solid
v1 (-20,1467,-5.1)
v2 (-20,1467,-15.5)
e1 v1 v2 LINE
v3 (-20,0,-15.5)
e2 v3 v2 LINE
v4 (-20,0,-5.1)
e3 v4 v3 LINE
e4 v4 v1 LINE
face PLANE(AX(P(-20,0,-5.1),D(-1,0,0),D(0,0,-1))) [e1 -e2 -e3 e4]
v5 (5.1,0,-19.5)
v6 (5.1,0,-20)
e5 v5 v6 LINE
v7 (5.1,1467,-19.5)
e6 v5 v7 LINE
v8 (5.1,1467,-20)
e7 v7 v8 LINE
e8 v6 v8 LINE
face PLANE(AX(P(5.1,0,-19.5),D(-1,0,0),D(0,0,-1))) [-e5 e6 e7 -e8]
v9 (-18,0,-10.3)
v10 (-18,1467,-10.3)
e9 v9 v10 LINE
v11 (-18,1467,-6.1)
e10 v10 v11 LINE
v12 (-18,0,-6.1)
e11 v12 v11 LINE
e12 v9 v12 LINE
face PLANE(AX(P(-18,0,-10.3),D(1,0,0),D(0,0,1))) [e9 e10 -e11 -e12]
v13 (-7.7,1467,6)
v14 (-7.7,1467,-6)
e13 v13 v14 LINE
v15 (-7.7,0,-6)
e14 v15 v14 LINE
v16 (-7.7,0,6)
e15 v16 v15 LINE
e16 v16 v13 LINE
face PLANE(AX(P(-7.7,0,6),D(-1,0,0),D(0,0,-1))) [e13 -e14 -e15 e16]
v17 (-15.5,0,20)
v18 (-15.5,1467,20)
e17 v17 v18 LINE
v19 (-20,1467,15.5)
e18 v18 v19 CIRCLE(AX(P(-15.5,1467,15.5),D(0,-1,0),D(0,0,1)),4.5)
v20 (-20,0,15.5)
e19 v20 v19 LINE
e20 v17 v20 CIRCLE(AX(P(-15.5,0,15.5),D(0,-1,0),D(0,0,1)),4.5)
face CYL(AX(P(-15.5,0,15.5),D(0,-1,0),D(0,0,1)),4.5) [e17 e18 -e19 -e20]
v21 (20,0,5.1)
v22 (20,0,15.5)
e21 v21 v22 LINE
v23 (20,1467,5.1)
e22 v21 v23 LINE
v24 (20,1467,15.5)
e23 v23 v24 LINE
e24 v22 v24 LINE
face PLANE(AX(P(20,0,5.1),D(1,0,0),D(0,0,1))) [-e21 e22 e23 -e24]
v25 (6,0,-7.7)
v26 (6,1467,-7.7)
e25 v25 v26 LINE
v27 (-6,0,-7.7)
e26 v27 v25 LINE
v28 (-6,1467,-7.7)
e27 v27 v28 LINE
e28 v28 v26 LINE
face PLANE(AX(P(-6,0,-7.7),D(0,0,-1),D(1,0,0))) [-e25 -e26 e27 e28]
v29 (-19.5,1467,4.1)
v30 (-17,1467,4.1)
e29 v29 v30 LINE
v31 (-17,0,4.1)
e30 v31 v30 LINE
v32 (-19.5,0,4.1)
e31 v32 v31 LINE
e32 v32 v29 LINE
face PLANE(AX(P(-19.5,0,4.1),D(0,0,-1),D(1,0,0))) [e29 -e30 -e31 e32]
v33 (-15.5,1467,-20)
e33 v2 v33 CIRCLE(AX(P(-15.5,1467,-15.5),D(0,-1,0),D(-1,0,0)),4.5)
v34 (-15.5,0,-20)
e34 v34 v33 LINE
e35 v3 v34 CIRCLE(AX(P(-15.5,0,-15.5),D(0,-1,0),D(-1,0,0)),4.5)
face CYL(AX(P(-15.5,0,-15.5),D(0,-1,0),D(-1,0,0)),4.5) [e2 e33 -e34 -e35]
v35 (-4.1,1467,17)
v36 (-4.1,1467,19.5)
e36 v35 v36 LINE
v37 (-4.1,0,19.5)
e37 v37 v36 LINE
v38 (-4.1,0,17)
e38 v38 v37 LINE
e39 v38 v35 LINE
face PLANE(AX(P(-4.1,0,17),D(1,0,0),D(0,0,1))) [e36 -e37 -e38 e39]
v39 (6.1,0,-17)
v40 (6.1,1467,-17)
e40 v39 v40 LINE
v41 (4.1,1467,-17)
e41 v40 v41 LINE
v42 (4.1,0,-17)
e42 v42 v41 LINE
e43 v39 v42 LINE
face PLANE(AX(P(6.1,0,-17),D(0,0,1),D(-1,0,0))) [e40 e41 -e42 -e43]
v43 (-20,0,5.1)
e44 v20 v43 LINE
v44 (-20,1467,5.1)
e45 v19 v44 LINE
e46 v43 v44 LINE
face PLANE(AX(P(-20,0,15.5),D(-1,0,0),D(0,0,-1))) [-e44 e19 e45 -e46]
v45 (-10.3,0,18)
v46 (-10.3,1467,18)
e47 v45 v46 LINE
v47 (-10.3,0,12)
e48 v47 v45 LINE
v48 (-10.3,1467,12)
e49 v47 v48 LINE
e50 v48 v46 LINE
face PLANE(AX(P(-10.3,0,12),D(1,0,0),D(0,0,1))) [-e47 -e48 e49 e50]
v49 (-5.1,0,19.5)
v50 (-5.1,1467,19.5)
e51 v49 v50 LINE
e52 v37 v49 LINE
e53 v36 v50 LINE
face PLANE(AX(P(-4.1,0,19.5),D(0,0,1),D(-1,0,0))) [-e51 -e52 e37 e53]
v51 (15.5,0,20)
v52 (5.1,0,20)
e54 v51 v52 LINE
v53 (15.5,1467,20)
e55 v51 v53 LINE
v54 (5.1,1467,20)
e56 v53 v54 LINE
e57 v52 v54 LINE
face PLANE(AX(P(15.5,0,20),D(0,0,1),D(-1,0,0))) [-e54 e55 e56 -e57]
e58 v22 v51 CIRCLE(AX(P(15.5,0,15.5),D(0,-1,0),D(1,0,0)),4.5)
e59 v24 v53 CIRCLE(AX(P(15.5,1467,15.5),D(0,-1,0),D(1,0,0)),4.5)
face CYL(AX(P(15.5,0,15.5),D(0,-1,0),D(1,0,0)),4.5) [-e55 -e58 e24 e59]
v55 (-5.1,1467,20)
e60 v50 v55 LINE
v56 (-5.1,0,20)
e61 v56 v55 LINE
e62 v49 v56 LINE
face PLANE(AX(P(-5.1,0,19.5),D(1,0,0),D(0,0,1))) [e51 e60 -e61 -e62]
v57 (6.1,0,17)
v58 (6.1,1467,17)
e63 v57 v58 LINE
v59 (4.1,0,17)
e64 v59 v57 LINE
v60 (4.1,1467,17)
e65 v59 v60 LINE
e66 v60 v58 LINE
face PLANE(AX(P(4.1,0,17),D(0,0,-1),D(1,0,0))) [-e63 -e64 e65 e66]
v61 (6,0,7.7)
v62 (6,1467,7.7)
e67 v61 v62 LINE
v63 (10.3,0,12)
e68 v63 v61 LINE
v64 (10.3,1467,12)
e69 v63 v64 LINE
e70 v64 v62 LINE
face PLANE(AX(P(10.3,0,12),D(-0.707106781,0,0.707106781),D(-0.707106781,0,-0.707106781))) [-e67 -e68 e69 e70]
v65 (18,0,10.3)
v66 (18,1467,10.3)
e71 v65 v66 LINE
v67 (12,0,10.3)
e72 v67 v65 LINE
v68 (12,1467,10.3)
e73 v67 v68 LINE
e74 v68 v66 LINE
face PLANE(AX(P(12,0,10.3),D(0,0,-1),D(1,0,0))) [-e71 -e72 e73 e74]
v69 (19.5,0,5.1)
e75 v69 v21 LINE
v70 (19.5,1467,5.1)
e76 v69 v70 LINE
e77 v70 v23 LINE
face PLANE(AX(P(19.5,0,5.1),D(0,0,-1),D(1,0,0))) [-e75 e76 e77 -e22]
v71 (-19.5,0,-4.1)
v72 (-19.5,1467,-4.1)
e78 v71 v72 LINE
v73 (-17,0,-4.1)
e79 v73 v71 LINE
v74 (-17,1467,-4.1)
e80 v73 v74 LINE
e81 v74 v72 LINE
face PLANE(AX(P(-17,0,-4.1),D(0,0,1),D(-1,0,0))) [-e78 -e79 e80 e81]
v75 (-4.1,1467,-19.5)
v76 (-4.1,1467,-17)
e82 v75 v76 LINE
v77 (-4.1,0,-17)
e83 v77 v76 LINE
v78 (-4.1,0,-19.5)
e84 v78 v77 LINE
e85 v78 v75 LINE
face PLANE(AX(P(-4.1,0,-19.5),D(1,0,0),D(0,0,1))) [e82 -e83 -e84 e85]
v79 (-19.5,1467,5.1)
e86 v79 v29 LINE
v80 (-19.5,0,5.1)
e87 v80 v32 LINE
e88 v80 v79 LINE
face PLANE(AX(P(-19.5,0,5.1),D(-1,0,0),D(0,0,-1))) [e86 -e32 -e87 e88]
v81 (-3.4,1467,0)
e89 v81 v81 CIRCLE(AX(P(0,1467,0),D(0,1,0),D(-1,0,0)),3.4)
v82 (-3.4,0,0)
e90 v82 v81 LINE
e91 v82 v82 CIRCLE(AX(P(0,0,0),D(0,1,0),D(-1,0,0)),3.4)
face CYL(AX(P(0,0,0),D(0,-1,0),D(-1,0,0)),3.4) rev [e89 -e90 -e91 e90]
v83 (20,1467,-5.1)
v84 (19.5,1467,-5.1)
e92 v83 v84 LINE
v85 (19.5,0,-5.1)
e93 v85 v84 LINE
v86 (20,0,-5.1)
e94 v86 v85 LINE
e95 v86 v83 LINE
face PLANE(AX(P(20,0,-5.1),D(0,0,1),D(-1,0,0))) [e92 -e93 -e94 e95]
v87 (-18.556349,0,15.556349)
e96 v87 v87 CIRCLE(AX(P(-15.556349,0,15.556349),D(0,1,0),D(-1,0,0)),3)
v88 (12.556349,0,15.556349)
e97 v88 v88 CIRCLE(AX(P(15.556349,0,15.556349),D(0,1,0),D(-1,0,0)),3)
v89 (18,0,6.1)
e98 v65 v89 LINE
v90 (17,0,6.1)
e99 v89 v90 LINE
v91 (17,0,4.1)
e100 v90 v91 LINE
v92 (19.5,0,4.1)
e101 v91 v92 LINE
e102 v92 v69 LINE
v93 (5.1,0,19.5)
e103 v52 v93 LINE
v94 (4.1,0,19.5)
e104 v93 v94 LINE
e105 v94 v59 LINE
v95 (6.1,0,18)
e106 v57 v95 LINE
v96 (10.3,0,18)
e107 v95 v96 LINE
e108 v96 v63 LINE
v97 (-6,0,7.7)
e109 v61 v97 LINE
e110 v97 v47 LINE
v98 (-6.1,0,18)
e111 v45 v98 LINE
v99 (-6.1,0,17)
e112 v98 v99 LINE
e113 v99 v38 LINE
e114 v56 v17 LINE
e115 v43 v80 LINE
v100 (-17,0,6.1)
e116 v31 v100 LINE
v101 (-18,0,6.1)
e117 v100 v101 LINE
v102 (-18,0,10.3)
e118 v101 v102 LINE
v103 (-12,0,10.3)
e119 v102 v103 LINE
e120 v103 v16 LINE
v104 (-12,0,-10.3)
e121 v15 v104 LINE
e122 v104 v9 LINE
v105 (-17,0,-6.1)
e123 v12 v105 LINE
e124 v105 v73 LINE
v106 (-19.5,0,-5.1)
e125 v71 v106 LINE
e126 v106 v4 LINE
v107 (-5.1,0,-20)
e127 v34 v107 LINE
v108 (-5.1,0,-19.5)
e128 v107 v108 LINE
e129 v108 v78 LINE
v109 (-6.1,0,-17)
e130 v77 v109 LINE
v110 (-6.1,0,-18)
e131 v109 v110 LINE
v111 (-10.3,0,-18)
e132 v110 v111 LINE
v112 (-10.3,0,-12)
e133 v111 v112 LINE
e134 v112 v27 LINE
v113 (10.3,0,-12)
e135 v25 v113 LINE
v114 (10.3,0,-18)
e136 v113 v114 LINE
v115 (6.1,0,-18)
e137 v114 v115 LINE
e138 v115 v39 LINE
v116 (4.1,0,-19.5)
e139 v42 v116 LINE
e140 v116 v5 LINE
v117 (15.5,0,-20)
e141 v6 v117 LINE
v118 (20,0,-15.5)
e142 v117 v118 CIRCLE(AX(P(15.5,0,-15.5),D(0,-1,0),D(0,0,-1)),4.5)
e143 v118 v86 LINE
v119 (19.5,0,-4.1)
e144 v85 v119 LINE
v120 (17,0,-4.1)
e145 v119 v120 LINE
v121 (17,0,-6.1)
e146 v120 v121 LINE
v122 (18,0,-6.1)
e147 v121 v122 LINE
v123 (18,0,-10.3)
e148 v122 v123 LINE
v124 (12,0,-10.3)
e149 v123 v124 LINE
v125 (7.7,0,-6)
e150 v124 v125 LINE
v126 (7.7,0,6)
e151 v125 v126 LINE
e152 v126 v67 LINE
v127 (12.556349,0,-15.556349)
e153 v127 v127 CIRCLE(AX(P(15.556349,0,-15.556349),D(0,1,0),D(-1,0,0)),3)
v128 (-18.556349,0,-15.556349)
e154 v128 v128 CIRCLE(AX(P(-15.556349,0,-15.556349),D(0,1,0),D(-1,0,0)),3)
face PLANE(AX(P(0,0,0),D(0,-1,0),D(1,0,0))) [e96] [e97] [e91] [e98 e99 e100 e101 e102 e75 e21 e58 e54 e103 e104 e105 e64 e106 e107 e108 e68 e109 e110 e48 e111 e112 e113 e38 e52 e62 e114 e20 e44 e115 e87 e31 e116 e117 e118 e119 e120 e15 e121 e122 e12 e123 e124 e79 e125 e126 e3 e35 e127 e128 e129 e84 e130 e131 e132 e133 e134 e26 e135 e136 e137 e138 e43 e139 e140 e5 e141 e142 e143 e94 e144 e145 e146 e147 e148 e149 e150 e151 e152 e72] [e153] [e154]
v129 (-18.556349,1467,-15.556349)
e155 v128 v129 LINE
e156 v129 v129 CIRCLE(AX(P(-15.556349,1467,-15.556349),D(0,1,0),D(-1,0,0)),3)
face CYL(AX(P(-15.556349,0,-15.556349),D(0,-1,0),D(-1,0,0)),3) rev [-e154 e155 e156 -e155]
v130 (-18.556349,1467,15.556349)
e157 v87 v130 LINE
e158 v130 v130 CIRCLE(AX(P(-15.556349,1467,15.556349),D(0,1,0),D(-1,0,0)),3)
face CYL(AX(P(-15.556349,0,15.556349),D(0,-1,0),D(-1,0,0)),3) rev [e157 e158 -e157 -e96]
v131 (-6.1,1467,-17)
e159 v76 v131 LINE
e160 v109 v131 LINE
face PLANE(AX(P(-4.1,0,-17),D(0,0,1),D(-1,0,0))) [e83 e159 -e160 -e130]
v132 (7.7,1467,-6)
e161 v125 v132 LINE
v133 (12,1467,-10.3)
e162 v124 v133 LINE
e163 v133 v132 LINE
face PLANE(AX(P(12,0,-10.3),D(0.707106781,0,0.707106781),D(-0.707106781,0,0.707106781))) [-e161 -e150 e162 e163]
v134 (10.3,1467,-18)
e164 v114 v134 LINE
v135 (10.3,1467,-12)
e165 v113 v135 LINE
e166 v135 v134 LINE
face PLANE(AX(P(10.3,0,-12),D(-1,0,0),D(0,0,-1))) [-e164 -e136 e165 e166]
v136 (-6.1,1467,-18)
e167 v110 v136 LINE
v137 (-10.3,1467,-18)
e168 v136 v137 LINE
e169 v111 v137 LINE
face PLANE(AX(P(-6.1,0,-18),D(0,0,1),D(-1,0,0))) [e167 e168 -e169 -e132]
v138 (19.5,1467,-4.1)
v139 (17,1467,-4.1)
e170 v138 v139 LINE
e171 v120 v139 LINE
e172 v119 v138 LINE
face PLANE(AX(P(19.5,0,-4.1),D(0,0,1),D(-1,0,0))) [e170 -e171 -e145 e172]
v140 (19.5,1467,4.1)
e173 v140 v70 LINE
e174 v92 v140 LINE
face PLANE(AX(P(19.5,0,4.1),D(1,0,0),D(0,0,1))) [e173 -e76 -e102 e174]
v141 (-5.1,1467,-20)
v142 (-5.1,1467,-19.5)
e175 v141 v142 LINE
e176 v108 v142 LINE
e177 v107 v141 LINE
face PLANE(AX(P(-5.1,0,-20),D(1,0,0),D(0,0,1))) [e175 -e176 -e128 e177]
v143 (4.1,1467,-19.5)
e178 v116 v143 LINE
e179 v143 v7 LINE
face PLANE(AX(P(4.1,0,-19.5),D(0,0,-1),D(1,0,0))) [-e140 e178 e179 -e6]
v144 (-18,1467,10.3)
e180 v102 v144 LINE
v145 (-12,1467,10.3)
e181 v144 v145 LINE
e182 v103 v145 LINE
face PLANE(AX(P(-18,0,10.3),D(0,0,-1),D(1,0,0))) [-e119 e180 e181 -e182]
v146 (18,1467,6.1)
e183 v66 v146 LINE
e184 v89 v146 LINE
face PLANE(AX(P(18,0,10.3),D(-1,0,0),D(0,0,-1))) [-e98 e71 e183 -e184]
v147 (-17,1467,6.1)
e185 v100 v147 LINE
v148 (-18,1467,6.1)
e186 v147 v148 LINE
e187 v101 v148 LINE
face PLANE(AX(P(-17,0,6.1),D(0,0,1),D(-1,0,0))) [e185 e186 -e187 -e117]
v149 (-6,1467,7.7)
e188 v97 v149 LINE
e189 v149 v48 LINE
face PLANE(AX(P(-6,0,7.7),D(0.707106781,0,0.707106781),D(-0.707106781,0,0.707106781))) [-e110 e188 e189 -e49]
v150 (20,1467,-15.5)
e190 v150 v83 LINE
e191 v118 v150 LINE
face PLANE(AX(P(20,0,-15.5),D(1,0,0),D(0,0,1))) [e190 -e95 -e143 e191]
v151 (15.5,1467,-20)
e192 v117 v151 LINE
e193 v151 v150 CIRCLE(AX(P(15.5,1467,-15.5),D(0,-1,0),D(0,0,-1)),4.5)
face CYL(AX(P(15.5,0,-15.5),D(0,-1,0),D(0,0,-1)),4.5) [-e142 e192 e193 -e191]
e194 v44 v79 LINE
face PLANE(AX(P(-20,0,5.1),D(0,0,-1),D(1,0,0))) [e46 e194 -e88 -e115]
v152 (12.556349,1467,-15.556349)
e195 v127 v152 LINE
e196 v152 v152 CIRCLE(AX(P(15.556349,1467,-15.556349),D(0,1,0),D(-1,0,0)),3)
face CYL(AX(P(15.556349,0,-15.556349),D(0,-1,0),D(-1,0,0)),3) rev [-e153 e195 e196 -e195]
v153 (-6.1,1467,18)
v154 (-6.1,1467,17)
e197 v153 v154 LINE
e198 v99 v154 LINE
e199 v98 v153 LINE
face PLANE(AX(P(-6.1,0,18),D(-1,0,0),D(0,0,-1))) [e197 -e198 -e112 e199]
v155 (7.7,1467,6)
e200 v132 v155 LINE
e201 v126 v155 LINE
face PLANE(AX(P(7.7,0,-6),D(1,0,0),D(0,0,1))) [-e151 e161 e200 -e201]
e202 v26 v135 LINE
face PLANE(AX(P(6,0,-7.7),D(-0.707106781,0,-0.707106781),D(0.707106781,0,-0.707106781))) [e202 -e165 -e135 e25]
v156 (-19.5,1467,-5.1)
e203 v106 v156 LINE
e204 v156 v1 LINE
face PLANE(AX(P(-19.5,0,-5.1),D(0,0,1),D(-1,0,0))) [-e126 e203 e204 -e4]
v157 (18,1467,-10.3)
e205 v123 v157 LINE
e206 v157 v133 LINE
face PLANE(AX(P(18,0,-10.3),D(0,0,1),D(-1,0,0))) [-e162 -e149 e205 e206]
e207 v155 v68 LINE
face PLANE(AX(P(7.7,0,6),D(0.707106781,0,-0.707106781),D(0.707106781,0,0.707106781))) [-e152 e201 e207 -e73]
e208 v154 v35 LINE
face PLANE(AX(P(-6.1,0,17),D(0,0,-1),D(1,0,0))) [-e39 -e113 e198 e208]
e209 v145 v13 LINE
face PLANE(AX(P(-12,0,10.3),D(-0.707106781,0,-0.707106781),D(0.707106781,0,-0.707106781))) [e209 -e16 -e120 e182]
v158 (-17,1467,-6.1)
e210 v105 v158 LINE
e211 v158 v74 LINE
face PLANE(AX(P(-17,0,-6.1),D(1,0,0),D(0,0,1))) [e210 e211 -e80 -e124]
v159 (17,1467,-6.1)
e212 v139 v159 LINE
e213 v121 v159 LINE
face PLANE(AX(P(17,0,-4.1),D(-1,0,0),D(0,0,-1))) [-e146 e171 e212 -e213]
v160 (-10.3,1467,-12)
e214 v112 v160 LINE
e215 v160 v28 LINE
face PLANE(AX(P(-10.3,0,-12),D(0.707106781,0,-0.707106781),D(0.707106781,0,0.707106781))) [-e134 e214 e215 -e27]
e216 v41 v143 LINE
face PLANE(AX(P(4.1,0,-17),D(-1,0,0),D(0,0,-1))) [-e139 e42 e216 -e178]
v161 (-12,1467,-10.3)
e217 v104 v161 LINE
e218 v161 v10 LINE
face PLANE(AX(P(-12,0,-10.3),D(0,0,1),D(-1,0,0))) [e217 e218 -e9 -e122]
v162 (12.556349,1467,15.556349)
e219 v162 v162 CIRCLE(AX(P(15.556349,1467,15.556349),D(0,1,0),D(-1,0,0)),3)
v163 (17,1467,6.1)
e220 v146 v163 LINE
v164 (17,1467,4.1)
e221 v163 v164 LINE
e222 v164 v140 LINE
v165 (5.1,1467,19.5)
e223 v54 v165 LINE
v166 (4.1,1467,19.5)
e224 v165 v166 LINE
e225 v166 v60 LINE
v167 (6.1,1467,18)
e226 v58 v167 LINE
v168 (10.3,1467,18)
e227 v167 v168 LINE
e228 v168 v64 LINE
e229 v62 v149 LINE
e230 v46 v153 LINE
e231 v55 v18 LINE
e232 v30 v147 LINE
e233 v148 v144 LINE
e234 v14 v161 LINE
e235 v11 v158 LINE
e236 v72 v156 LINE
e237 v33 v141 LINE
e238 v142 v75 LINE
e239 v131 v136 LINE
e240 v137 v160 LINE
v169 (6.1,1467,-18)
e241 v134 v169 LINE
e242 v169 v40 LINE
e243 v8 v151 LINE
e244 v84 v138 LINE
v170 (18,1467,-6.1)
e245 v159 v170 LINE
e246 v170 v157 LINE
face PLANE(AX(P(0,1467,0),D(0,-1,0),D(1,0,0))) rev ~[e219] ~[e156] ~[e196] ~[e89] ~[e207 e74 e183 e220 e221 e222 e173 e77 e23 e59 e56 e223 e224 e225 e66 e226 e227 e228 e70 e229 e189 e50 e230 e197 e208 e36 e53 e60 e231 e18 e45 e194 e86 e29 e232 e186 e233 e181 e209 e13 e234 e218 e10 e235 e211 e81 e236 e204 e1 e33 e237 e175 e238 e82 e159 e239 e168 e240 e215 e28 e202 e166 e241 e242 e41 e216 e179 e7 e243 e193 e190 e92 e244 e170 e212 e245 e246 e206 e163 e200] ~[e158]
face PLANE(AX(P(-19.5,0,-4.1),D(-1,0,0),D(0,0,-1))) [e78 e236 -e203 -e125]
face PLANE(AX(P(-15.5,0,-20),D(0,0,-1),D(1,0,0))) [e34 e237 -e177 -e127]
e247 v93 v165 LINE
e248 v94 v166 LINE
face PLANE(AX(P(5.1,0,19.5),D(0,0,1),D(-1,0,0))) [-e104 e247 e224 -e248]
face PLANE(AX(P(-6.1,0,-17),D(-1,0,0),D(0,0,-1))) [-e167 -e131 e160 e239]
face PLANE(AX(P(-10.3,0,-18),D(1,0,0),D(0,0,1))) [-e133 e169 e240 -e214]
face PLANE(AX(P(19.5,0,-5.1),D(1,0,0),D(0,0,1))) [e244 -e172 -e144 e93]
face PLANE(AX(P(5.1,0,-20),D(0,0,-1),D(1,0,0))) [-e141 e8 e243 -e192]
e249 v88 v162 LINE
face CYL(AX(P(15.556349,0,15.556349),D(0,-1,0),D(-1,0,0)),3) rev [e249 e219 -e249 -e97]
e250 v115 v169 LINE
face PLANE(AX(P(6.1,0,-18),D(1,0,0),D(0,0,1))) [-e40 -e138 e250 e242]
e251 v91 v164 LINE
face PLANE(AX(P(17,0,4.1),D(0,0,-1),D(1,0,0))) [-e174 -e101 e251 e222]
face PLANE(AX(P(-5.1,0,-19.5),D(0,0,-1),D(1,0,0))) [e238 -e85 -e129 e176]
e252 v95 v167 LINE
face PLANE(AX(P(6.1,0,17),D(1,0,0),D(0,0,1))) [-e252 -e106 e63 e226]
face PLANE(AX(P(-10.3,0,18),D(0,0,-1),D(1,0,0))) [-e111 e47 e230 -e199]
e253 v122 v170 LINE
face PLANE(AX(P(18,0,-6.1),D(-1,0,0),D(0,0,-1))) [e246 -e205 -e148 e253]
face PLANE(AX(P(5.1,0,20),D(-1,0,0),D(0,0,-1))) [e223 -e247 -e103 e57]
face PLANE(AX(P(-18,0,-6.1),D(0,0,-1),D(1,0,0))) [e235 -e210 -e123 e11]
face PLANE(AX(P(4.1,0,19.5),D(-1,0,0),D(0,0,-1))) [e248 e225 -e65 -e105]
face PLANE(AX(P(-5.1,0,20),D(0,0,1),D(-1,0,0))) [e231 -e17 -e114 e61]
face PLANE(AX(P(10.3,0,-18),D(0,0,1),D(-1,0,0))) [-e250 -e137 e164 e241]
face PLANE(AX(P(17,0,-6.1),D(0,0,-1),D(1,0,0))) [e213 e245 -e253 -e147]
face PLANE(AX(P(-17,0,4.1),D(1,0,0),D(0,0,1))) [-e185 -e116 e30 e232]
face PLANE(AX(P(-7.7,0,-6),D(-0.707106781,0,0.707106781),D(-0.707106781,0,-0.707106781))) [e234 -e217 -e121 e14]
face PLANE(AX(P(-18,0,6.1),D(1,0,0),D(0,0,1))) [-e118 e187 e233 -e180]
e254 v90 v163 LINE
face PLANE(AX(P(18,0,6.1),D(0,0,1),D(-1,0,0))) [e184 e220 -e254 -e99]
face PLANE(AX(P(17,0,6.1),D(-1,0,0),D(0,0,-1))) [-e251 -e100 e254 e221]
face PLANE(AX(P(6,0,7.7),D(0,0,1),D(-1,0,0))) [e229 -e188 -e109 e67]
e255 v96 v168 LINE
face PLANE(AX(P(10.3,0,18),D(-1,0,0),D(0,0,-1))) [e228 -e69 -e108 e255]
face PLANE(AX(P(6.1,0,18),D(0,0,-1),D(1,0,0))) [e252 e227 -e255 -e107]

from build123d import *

# Parameters (mm, degrees)
SKETCH16_R     = 3.4
SKETCH16_R_2   = 3
MEMBER_1_DEPTH = 1467


with BuildPart() as part:
    # Sketch16 → Member 1 (new body)
    with BuildSketch(Plane(origin=(0, 0, 0), x_dir=(-1, 0, 0), z_dir=(0, 1, 0))):
        with BuildLine():
            Line((-5.1, 20), (-5.1, 19.5))
            Line((-5.1, 19.5), (-4.1, 19.5))
            Line((-4.1, 19.5), (-4.1, 17))
            Line((-4.1, 17), (-6.1, 17))
            Line((-6.1, 17), (-6.1, 18))
            Line((-6.1, 18), (-10.3, 18))
            Line((-10.3, 18), (-10.3, 12))
            Line((-10.3, 12), (-6, 7.7))
            Line((-6, 7.7), (6, 7.7))
            Line((6, 7.7), (10.3, 12))
            Line((10.3, 12), (10.3, 18))
            Line((10.3, 18), (6.1, 18))
            Line((6.1, 18), (6.1, 17))
            Line((6.1, 17), (4.1, 17))
            Line((4.1, 17), (4.1, 19.5))
            Line((4.1, 19.5), (5.1, 19.5))
            Line((5.1, 19.5), (5.1, 20))
            Line((5.1, 20), (15.5, 20))
            ThreePointArc((15.5, 20), (18.681980515, 18.681980515), (20, 15.5))
            Line((20, 15.5), (20, 5.1))
            Line((20, 5.1), (19.5, 5.1))
            Line((19.5, 5.1), (19.5, 4.1))
            Line((19.5, 4.1), (17, 4.1))
            Line((17, 4.1), (17, 6.1))
            Line((17, 6.1), (18, 6.1))
            Line((18, 6.1), (18, 10.3))
            Line((18, 10.3), (12, 10.3))
            Line((12, 10.3), (7.7, 6))
            Line((7.7, 6), (7.7, -6))
            Line((7.7, -6), (12, -10.3))
            Line((12, -10.3), (18, -10.3))
            Line((18, -10.3), (18, -6.1))
            Line((18, -6.1), (17, -6.1))
            Line((17, -6.1), (17, -4.1))
            Line((17, -4.1), (19.5, -4.1))
            Line((19.5, -4.1), (19.5, -5.1))
            Line((19.5, -5.1), (20, -5.1))
            Line((20, -5.1), (20, -15.5))
            ThreePointArc((20, -15.5), (18.681980515, -18.681980515), (15.5, -20))
            Line((15.5, -20), (5.1, -20))
            Line((5.1, -20), (5.1, -19.5))
            Line((5.1, -19.5), (4.1, -19.5))
            Line((4.1, -19.5), (4.1, -17))
            Line((4.1, -17), (6.1, -17))
            Line((6.1, -17), (6.1, -18))
            Line((6.1, -18), (10.3, -18))
            Line((10.3, -18), (10.3, -12))
            Line((10.3, -12), (6, -7.7))
            Line((6, -7.7), (-6, -7.7))
            Line((-6, -7.7), (-10.3, -12))
            Line((-10.3, -12), (-10.3, -18))
            Line((-10.3, -18), (-6.1, -18))
            Line((-6.1, -18), (-6.1, -17))
            Line((-6.1, -17), (-4.1, -17))
            Line((-4.1, -17), (-4.1, -19.5))
            Line((-4.1, -19.5), (-5.1, -19.5))
            Line((-5.1, -19.5), (-5.1, -20))
            Line((-5.1, -20), (-15.5, -20))
            ThreePointArc((-15.5, -20), (-18.681980515, -18.681980515), (-20, -15.5))
            Line((-20, -15.5), (-20, -5.1))
            Line((-20, -5.1), (-19.5, -5.1))
            Line((-19.5, -5.1), (-19.5, -4.1))
            Line((-19.5, -4.1), (-17, -4.1))
            Line((-17, -4.1), (-17, -6.1))
            Line((-17, -6.1), (-18, -6.1))
            Line((-18, -6.1), (-18, -10.3))
            Line((-18, -10.3), (-12, -10.3))
            Line((-12, -10.3), (-7.7, -6))
            Line((-7.7, -6), (-7.7, 6))
            Line((-7.7, 6), (-12, 10.3))
            Line((-12, 10.3), (-18, 10.3))
            Line((-18, 10.3), (-18, 6.1))
            Line((-18, 6.1), (-17, 6.1))
            Line((-17, 6.1), (-17, 4.1))
            Line((-17, 4.1), (-19.5, 4.1))
            Line((-19.5, 4.1), (-19.5, 5.1))
            Line((-19.5, 5.1), (-20, 5.1))
            Line((-20, 5.1), (-20, 15.5))
            ThreePointArc((-20, 15.5), (-18.681980515, 18.681980515), (-15.5, 20))
            Line((-15.5, 20), (-5.1, 20))
        make_face()
        Circle(SKETCH16_R, mode=Mode.SUBTRACT)
        with Locations((-15.556349186, 15.556349186)):
            Circle(SKETCH16_R_2, mode=Mode.SUBTRACT)
        with Locations((15.556349186, 15.556349186)):
            Circle(SKETCH16_R_2, mode=Mode.SUBTRACT)
        with Locations((15.556349186, -15.556349186)):
            Circle(SKETCH16_R_2, mode=Mode.SUBTRACT)
        with Locations((-15.556349186, -15.556349186)):
            Circle(SKETCH16_R_2, mode=Mode.SUBTRACT)
    extrude(amount=MEMBER_1_DEPTH)


solid = part.part
